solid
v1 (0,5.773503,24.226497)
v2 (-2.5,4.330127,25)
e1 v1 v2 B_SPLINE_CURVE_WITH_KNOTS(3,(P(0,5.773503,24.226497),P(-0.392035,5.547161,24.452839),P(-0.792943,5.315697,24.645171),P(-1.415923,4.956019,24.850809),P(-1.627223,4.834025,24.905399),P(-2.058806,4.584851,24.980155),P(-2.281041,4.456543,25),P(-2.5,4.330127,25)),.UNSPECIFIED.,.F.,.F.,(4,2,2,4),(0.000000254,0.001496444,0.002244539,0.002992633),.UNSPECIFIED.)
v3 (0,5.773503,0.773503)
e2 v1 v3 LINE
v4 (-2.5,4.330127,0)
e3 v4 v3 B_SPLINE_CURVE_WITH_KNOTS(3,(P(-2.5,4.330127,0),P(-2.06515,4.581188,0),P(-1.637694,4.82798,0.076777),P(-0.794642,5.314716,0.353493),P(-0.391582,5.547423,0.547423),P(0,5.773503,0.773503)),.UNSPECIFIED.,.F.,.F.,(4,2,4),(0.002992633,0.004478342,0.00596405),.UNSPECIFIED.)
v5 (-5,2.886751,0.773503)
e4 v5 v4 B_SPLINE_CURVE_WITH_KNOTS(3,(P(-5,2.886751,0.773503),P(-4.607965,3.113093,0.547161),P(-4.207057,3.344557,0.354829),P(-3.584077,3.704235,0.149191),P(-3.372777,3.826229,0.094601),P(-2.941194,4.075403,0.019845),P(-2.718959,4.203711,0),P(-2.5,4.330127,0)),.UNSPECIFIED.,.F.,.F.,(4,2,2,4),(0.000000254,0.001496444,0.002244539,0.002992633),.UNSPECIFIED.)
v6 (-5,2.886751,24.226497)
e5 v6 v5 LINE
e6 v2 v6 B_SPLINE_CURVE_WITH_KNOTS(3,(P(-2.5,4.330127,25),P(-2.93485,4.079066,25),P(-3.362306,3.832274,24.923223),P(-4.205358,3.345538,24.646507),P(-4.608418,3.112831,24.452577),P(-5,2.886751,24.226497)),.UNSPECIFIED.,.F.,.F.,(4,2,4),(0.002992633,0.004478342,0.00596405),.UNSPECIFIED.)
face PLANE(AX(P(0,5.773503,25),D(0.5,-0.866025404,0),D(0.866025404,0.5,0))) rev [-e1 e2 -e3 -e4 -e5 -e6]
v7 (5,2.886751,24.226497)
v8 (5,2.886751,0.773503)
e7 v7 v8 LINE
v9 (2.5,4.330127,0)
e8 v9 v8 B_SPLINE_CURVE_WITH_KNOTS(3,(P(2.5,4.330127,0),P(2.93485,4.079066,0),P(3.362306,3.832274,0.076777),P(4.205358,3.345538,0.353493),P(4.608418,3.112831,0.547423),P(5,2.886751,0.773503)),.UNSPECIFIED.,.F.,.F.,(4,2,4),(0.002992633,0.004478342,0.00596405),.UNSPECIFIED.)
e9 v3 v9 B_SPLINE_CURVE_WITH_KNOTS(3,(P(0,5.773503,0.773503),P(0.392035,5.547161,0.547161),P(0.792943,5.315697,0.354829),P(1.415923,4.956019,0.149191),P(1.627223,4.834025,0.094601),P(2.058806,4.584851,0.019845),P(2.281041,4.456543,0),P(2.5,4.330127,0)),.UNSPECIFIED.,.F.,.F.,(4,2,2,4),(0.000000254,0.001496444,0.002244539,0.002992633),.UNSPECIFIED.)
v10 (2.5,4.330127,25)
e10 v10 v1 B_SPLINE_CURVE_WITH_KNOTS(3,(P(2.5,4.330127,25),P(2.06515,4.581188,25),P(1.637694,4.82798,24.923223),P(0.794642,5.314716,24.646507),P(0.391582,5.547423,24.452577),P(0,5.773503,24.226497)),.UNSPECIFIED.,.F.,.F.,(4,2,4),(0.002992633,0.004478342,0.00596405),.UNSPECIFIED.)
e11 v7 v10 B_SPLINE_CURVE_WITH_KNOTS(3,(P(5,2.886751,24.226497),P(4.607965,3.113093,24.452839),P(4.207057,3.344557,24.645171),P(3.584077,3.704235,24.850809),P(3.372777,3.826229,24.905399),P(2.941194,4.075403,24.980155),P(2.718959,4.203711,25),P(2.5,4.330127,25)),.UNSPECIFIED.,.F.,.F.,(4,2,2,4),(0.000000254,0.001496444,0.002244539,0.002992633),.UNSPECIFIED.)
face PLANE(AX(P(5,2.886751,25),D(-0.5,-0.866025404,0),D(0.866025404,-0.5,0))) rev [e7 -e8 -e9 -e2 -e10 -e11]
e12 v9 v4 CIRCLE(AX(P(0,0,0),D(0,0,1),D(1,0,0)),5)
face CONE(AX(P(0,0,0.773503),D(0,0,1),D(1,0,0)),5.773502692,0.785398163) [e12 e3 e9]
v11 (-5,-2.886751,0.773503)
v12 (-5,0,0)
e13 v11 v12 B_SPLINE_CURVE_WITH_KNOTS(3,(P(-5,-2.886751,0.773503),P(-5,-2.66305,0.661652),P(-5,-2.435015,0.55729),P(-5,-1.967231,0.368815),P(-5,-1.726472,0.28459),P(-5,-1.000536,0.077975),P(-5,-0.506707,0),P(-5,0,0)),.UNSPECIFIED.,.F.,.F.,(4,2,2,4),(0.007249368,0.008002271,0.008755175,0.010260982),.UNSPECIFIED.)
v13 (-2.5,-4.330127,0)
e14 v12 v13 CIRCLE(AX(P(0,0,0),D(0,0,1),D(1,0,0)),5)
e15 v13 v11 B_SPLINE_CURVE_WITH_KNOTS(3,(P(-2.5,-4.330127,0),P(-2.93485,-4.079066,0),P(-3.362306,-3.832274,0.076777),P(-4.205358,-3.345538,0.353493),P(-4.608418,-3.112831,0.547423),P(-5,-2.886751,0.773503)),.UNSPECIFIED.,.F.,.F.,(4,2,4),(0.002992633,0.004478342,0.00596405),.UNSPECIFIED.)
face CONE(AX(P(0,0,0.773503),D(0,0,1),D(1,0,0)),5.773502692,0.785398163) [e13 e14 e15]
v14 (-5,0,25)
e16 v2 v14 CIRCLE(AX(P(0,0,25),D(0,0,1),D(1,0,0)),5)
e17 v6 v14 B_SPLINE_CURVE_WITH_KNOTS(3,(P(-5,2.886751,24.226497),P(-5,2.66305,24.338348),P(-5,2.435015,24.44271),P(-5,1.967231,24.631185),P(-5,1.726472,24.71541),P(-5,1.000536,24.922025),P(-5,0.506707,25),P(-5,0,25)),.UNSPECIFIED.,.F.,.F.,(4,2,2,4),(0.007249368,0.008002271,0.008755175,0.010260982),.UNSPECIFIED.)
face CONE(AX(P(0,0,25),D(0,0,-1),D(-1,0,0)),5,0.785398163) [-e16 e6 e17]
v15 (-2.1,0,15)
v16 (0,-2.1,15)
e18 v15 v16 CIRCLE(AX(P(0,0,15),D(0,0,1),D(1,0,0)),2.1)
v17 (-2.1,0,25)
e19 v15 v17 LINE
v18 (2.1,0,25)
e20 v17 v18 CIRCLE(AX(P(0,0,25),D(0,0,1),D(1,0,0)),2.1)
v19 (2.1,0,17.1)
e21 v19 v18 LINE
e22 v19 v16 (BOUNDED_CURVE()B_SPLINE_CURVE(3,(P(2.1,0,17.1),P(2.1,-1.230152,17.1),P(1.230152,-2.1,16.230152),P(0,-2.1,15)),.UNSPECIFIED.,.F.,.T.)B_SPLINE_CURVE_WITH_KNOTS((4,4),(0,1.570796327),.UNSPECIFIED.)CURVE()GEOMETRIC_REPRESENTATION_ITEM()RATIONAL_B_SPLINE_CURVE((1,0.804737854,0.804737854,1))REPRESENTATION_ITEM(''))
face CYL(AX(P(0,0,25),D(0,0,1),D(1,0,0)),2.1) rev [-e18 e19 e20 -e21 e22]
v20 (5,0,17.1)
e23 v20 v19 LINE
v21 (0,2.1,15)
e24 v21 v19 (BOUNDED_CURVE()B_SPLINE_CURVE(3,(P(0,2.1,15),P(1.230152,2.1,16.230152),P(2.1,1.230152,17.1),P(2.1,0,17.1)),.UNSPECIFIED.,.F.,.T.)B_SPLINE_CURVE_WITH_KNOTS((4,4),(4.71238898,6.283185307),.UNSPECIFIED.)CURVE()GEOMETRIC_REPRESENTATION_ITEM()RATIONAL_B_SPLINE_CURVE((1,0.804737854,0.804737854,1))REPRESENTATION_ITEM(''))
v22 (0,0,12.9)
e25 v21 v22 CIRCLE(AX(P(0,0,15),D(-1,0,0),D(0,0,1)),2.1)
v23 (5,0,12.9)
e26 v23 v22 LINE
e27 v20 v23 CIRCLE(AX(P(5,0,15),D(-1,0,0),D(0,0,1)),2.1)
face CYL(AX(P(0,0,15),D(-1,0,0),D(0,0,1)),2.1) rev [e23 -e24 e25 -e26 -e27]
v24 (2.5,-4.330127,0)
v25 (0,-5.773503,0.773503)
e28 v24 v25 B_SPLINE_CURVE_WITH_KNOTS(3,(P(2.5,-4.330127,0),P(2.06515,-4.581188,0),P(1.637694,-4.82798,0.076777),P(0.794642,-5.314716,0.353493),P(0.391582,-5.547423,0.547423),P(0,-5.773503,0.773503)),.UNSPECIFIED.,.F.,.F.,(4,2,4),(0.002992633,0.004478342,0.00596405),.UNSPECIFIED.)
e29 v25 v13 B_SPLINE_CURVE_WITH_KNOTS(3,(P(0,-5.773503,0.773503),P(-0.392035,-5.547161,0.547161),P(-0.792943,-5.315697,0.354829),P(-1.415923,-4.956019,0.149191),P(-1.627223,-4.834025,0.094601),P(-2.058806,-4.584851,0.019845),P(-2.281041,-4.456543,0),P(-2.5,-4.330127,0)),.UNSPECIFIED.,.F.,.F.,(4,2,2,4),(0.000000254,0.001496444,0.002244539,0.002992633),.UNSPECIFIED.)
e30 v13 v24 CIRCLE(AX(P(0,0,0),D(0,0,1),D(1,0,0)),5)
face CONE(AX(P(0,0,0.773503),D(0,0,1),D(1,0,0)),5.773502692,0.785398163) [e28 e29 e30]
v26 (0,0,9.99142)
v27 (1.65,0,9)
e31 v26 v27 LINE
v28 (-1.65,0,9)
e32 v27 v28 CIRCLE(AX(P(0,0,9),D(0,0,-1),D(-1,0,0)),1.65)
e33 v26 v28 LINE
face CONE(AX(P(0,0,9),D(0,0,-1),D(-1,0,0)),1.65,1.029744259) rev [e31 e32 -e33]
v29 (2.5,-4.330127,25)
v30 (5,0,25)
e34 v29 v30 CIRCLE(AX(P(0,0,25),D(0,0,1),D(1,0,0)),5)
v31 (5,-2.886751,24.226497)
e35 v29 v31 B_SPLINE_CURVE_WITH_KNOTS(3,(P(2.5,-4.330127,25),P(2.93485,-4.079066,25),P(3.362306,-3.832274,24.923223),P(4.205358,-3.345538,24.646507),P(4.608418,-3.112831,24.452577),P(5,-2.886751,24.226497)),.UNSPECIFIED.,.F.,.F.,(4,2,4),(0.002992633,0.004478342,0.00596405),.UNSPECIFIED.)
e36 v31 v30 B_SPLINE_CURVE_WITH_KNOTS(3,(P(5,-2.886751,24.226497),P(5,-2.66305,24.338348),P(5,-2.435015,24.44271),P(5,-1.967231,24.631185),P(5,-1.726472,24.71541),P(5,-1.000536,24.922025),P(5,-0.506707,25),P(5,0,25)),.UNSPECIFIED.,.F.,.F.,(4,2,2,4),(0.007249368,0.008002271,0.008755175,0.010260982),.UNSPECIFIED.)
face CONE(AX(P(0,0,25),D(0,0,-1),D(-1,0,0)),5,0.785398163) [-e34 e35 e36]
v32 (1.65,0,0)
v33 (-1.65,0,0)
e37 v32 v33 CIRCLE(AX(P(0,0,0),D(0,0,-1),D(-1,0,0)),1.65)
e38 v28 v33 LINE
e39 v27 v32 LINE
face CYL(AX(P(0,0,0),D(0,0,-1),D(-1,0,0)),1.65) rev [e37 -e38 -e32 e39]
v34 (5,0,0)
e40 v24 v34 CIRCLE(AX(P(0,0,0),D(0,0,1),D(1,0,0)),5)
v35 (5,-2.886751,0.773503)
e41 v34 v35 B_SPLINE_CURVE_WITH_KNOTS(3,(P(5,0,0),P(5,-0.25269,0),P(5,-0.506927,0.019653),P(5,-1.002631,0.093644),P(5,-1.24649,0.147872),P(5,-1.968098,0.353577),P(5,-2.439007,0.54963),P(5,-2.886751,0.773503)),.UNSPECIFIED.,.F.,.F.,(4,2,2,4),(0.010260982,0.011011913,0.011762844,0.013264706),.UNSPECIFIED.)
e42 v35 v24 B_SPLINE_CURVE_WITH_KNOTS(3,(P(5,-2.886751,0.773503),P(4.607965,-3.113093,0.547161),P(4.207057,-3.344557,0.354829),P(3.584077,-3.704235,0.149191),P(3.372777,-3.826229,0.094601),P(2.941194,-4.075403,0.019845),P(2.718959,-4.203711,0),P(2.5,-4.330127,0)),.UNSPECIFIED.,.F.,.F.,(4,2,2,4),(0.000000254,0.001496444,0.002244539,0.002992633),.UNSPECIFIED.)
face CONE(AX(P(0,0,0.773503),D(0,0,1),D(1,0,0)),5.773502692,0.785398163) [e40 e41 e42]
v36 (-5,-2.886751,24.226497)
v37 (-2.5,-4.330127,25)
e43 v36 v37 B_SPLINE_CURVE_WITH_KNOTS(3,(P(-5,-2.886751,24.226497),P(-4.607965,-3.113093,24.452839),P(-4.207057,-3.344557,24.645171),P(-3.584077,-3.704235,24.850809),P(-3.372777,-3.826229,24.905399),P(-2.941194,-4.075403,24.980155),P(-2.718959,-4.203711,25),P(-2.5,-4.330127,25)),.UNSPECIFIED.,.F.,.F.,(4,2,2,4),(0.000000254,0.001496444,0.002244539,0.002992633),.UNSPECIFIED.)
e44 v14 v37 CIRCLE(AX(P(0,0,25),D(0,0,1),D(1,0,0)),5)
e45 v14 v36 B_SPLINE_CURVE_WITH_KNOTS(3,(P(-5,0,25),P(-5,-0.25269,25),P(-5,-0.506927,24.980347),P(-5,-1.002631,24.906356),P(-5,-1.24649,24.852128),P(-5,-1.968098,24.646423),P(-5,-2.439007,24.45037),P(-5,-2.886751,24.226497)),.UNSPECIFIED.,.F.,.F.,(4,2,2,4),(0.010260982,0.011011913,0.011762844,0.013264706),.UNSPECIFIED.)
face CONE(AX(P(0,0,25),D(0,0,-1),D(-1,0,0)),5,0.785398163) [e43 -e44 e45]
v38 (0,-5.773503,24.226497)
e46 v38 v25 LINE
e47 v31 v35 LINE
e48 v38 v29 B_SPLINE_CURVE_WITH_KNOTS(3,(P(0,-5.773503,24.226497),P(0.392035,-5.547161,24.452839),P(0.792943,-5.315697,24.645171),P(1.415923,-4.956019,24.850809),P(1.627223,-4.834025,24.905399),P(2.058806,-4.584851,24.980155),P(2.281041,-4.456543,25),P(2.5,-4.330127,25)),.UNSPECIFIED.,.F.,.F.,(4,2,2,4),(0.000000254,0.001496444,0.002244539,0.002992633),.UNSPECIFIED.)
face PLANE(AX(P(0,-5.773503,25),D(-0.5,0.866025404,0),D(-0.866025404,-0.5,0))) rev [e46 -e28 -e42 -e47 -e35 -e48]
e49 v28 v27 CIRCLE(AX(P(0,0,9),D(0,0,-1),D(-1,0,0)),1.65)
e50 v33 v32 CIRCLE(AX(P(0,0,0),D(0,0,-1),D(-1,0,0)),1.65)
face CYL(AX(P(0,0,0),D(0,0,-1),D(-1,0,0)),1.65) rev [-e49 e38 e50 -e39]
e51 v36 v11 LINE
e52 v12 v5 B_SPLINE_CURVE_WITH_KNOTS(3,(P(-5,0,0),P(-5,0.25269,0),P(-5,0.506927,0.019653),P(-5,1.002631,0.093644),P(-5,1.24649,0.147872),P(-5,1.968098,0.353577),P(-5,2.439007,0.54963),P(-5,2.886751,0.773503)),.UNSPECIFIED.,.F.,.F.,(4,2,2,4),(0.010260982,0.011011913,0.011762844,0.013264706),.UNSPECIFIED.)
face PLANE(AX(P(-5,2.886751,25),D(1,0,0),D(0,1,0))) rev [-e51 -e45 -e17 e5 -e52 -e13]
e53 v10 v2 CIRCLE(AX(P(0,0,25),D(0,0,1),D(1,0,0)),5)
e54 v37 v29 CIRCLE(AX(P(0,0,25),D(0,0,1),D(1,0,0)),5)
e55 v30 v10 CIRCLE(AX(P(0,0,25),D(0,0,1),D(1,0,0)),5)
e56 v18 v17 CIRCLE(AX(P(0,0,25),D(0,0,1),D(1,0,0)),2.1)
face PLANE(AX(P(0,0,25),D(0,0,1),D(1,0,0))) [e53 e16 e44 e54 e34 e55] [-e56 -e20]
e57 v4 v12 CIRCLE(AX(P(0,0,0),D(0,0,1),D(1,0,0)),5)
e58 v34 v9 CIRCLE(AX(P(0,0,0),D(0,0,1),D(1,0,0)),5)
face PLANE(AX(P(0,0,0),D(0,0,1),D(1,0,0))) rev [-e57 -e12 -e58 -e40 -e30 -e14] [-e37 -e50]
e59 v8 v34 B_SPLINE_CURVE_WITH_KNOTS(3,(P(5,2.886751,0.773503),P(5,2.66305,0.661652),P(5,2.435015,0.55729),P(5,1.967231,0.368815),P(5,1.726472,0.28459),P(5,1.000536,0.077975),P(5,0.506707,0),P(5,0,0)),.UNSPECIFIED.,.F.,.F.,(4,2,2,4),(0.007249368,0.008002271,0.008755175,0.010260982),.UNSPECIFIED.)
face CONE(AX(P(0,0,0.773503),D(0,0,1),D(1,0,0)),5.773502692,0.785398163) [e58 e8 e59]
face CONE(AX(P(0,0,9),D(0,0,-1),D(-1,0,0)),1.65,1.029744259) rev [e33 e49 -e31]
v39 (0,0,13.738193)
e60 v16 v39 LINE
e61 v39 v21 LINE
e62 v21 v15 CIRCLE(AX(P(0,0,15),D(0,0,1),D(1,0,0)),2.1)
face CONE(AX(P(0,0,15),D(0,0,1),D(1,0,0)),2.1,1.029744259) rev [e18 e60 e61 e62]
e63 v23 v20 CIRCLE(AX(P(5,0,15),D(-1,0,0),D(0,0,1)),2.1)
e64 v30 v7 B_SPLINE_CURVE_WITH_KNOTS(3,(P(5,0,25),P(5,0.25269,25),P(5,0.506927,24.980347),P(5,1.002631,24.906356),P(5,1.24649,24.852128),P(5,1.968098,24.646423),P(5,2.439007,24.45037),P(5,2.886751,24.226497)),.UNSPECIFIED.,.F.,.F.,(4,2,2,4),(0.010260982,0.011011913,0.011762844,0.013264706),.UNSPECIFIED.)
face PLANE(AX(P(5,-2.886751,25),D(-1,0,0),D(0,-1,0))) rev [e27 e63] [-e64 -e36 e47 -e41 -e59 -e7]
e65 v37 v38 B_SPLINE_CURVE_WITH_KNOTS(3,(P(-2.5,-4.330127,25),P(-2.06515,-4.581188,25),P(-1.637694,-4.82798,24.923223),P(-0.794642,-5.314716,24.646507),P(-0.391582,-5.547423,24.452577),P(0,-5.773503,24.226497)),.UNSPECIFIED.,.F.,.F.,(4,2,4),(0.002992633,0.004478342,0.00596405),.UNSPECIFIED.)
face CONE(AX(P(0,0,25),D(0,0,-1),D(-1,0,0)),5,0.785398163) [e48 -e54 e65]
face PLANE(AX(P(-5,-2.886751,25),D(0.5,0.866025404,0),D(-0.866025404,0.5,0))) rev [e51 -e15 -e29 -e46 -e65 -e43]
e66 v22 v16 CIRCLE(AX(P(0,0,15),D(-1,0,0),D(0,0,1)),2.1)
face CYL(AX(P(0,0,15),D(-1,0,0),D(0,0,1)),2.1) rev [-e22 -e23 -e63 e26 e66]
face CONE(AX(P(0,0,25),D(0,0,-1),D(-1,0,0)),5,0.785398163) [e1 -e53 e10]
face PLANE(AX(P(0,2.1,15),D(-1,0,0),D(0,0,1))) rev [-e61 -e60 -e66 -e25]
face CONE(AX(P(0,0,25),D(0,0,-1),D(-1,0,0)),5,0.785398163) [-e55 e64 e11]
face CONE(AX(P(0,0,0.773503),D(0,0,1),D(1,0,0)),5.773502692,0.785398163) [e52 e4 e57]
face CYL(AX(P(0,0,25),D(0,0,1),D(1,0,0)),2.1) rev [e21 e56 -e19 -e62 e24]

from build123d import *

# Parameters (mm, degrees)
BOSS_EXTRUDE1_DEPTH   = 25
M5_TAPPED_HOLE3_D     = 4.2
M5_TAPPED_HOLE3_DEPTH = 10
M5_TAPPED_HOLE3_TIP   = 1.2618073
M4_TAPPED_HOLE1_D     = 3.3
M4_TAPPED_HOLE1_DEPTH = 9
M4_TAPPED_HOLE1_TIP   = 0.991420021
SKETCH7_W             = 2.1
SKETCH7_H             = 5


with BuildPart() as part:
    # Sketch1 → Boss-Extrude1 (new body)
    with BuildSketch(Plane.XY):
        Polygon((0, 5.773502692), (-5, 2.886751346), (-5, -2.886751346), (0, -5.773502692), (5, -2.886751346), (5, 2.886751346), align=None)
    extrude(amount=BOSS_EXTRUDE1_DEPTH)

    # M5 Tapped Hole3
    with Locations(Plane.XY.offset(25)):
        with Locations((0, 0)):
            Hole(M5_TAPPED_HOLE3_D / 2, depth=M5_TAPPED_HOLE3_DEPTH)
            with Locations((0, 0, -(M5_TAPPED_HOLE3_DEPTH + M5_TAPPED_HOLE3_TIP / 2))):  # 118° drill point
                Cone(0, M5_TAPPED_HOLE3_D / 2, M5_TAPPED_HOLE3_TIP, mode=Mode.SUBTRACT)

    # M4 Tapped Hole1
    with Locations(Plane(origin=(0, 0, 0), x_dir=(-1, 0, 0), z_dir=(0, 0, -1))):
        with Locations((0, 0)):
            Hole(M4_TAPPED_HOLE1_D / 2, depth=M4_TAPPED_HOLE1_DEPTH)
            with Locations((0, 0, -(M4_TAPPED_HOLE1_DEPTH + M4_TAPPED_HOLE1_TIP / 2))):  # 118° drill point
                Cone(0, M4_TAPPED_HOLE1_D / 2, M4_TAPPED_HOLE1_TIP, mode=Mode.SUBTRACT)

    # Sketch7 → M5 Tapped Hole2 (revolve, cut)
    with BuildSketch(Plane(origin=(0, 0, 15), x_dir=(0, 0, 1), z_dir=(0, 1, 0))):
        with Locations((1.05, 2.5)):
            Rectangle(SKETCH7_W, SKETCH7_H)
    revolve(axis=Axis((-6.35, 0, 15), (1, 0, 0)), mode=Mode.SUBTRACT)

    # Sketch8 → Cut-Revolve1 (revolve, cut)
    with BuildSketch(Plane(origin=(0, 0, 0), x_dir=(0, 0, -1), z_dir=(1, 0, 0)), mode=Mode.PRIVATE) as cut_revolve1_sk:
        Polygon((-25, 5), (-25, 5.773502692), (-24.226497308, 5.773502692), align=None)
        Polygon((0, 5), (0, 5.773502692), (-0.773502692, 5.773502692), align=None)
    revolve(cut_revolve1_sk.sketch.rotate(Axis((0, 0, 25), (0, 0, -1)), 90), axis=Axis((0, 0, 25), (0, 0, -1)), mode=Mode.SUBTRACT)


solid = part.part
